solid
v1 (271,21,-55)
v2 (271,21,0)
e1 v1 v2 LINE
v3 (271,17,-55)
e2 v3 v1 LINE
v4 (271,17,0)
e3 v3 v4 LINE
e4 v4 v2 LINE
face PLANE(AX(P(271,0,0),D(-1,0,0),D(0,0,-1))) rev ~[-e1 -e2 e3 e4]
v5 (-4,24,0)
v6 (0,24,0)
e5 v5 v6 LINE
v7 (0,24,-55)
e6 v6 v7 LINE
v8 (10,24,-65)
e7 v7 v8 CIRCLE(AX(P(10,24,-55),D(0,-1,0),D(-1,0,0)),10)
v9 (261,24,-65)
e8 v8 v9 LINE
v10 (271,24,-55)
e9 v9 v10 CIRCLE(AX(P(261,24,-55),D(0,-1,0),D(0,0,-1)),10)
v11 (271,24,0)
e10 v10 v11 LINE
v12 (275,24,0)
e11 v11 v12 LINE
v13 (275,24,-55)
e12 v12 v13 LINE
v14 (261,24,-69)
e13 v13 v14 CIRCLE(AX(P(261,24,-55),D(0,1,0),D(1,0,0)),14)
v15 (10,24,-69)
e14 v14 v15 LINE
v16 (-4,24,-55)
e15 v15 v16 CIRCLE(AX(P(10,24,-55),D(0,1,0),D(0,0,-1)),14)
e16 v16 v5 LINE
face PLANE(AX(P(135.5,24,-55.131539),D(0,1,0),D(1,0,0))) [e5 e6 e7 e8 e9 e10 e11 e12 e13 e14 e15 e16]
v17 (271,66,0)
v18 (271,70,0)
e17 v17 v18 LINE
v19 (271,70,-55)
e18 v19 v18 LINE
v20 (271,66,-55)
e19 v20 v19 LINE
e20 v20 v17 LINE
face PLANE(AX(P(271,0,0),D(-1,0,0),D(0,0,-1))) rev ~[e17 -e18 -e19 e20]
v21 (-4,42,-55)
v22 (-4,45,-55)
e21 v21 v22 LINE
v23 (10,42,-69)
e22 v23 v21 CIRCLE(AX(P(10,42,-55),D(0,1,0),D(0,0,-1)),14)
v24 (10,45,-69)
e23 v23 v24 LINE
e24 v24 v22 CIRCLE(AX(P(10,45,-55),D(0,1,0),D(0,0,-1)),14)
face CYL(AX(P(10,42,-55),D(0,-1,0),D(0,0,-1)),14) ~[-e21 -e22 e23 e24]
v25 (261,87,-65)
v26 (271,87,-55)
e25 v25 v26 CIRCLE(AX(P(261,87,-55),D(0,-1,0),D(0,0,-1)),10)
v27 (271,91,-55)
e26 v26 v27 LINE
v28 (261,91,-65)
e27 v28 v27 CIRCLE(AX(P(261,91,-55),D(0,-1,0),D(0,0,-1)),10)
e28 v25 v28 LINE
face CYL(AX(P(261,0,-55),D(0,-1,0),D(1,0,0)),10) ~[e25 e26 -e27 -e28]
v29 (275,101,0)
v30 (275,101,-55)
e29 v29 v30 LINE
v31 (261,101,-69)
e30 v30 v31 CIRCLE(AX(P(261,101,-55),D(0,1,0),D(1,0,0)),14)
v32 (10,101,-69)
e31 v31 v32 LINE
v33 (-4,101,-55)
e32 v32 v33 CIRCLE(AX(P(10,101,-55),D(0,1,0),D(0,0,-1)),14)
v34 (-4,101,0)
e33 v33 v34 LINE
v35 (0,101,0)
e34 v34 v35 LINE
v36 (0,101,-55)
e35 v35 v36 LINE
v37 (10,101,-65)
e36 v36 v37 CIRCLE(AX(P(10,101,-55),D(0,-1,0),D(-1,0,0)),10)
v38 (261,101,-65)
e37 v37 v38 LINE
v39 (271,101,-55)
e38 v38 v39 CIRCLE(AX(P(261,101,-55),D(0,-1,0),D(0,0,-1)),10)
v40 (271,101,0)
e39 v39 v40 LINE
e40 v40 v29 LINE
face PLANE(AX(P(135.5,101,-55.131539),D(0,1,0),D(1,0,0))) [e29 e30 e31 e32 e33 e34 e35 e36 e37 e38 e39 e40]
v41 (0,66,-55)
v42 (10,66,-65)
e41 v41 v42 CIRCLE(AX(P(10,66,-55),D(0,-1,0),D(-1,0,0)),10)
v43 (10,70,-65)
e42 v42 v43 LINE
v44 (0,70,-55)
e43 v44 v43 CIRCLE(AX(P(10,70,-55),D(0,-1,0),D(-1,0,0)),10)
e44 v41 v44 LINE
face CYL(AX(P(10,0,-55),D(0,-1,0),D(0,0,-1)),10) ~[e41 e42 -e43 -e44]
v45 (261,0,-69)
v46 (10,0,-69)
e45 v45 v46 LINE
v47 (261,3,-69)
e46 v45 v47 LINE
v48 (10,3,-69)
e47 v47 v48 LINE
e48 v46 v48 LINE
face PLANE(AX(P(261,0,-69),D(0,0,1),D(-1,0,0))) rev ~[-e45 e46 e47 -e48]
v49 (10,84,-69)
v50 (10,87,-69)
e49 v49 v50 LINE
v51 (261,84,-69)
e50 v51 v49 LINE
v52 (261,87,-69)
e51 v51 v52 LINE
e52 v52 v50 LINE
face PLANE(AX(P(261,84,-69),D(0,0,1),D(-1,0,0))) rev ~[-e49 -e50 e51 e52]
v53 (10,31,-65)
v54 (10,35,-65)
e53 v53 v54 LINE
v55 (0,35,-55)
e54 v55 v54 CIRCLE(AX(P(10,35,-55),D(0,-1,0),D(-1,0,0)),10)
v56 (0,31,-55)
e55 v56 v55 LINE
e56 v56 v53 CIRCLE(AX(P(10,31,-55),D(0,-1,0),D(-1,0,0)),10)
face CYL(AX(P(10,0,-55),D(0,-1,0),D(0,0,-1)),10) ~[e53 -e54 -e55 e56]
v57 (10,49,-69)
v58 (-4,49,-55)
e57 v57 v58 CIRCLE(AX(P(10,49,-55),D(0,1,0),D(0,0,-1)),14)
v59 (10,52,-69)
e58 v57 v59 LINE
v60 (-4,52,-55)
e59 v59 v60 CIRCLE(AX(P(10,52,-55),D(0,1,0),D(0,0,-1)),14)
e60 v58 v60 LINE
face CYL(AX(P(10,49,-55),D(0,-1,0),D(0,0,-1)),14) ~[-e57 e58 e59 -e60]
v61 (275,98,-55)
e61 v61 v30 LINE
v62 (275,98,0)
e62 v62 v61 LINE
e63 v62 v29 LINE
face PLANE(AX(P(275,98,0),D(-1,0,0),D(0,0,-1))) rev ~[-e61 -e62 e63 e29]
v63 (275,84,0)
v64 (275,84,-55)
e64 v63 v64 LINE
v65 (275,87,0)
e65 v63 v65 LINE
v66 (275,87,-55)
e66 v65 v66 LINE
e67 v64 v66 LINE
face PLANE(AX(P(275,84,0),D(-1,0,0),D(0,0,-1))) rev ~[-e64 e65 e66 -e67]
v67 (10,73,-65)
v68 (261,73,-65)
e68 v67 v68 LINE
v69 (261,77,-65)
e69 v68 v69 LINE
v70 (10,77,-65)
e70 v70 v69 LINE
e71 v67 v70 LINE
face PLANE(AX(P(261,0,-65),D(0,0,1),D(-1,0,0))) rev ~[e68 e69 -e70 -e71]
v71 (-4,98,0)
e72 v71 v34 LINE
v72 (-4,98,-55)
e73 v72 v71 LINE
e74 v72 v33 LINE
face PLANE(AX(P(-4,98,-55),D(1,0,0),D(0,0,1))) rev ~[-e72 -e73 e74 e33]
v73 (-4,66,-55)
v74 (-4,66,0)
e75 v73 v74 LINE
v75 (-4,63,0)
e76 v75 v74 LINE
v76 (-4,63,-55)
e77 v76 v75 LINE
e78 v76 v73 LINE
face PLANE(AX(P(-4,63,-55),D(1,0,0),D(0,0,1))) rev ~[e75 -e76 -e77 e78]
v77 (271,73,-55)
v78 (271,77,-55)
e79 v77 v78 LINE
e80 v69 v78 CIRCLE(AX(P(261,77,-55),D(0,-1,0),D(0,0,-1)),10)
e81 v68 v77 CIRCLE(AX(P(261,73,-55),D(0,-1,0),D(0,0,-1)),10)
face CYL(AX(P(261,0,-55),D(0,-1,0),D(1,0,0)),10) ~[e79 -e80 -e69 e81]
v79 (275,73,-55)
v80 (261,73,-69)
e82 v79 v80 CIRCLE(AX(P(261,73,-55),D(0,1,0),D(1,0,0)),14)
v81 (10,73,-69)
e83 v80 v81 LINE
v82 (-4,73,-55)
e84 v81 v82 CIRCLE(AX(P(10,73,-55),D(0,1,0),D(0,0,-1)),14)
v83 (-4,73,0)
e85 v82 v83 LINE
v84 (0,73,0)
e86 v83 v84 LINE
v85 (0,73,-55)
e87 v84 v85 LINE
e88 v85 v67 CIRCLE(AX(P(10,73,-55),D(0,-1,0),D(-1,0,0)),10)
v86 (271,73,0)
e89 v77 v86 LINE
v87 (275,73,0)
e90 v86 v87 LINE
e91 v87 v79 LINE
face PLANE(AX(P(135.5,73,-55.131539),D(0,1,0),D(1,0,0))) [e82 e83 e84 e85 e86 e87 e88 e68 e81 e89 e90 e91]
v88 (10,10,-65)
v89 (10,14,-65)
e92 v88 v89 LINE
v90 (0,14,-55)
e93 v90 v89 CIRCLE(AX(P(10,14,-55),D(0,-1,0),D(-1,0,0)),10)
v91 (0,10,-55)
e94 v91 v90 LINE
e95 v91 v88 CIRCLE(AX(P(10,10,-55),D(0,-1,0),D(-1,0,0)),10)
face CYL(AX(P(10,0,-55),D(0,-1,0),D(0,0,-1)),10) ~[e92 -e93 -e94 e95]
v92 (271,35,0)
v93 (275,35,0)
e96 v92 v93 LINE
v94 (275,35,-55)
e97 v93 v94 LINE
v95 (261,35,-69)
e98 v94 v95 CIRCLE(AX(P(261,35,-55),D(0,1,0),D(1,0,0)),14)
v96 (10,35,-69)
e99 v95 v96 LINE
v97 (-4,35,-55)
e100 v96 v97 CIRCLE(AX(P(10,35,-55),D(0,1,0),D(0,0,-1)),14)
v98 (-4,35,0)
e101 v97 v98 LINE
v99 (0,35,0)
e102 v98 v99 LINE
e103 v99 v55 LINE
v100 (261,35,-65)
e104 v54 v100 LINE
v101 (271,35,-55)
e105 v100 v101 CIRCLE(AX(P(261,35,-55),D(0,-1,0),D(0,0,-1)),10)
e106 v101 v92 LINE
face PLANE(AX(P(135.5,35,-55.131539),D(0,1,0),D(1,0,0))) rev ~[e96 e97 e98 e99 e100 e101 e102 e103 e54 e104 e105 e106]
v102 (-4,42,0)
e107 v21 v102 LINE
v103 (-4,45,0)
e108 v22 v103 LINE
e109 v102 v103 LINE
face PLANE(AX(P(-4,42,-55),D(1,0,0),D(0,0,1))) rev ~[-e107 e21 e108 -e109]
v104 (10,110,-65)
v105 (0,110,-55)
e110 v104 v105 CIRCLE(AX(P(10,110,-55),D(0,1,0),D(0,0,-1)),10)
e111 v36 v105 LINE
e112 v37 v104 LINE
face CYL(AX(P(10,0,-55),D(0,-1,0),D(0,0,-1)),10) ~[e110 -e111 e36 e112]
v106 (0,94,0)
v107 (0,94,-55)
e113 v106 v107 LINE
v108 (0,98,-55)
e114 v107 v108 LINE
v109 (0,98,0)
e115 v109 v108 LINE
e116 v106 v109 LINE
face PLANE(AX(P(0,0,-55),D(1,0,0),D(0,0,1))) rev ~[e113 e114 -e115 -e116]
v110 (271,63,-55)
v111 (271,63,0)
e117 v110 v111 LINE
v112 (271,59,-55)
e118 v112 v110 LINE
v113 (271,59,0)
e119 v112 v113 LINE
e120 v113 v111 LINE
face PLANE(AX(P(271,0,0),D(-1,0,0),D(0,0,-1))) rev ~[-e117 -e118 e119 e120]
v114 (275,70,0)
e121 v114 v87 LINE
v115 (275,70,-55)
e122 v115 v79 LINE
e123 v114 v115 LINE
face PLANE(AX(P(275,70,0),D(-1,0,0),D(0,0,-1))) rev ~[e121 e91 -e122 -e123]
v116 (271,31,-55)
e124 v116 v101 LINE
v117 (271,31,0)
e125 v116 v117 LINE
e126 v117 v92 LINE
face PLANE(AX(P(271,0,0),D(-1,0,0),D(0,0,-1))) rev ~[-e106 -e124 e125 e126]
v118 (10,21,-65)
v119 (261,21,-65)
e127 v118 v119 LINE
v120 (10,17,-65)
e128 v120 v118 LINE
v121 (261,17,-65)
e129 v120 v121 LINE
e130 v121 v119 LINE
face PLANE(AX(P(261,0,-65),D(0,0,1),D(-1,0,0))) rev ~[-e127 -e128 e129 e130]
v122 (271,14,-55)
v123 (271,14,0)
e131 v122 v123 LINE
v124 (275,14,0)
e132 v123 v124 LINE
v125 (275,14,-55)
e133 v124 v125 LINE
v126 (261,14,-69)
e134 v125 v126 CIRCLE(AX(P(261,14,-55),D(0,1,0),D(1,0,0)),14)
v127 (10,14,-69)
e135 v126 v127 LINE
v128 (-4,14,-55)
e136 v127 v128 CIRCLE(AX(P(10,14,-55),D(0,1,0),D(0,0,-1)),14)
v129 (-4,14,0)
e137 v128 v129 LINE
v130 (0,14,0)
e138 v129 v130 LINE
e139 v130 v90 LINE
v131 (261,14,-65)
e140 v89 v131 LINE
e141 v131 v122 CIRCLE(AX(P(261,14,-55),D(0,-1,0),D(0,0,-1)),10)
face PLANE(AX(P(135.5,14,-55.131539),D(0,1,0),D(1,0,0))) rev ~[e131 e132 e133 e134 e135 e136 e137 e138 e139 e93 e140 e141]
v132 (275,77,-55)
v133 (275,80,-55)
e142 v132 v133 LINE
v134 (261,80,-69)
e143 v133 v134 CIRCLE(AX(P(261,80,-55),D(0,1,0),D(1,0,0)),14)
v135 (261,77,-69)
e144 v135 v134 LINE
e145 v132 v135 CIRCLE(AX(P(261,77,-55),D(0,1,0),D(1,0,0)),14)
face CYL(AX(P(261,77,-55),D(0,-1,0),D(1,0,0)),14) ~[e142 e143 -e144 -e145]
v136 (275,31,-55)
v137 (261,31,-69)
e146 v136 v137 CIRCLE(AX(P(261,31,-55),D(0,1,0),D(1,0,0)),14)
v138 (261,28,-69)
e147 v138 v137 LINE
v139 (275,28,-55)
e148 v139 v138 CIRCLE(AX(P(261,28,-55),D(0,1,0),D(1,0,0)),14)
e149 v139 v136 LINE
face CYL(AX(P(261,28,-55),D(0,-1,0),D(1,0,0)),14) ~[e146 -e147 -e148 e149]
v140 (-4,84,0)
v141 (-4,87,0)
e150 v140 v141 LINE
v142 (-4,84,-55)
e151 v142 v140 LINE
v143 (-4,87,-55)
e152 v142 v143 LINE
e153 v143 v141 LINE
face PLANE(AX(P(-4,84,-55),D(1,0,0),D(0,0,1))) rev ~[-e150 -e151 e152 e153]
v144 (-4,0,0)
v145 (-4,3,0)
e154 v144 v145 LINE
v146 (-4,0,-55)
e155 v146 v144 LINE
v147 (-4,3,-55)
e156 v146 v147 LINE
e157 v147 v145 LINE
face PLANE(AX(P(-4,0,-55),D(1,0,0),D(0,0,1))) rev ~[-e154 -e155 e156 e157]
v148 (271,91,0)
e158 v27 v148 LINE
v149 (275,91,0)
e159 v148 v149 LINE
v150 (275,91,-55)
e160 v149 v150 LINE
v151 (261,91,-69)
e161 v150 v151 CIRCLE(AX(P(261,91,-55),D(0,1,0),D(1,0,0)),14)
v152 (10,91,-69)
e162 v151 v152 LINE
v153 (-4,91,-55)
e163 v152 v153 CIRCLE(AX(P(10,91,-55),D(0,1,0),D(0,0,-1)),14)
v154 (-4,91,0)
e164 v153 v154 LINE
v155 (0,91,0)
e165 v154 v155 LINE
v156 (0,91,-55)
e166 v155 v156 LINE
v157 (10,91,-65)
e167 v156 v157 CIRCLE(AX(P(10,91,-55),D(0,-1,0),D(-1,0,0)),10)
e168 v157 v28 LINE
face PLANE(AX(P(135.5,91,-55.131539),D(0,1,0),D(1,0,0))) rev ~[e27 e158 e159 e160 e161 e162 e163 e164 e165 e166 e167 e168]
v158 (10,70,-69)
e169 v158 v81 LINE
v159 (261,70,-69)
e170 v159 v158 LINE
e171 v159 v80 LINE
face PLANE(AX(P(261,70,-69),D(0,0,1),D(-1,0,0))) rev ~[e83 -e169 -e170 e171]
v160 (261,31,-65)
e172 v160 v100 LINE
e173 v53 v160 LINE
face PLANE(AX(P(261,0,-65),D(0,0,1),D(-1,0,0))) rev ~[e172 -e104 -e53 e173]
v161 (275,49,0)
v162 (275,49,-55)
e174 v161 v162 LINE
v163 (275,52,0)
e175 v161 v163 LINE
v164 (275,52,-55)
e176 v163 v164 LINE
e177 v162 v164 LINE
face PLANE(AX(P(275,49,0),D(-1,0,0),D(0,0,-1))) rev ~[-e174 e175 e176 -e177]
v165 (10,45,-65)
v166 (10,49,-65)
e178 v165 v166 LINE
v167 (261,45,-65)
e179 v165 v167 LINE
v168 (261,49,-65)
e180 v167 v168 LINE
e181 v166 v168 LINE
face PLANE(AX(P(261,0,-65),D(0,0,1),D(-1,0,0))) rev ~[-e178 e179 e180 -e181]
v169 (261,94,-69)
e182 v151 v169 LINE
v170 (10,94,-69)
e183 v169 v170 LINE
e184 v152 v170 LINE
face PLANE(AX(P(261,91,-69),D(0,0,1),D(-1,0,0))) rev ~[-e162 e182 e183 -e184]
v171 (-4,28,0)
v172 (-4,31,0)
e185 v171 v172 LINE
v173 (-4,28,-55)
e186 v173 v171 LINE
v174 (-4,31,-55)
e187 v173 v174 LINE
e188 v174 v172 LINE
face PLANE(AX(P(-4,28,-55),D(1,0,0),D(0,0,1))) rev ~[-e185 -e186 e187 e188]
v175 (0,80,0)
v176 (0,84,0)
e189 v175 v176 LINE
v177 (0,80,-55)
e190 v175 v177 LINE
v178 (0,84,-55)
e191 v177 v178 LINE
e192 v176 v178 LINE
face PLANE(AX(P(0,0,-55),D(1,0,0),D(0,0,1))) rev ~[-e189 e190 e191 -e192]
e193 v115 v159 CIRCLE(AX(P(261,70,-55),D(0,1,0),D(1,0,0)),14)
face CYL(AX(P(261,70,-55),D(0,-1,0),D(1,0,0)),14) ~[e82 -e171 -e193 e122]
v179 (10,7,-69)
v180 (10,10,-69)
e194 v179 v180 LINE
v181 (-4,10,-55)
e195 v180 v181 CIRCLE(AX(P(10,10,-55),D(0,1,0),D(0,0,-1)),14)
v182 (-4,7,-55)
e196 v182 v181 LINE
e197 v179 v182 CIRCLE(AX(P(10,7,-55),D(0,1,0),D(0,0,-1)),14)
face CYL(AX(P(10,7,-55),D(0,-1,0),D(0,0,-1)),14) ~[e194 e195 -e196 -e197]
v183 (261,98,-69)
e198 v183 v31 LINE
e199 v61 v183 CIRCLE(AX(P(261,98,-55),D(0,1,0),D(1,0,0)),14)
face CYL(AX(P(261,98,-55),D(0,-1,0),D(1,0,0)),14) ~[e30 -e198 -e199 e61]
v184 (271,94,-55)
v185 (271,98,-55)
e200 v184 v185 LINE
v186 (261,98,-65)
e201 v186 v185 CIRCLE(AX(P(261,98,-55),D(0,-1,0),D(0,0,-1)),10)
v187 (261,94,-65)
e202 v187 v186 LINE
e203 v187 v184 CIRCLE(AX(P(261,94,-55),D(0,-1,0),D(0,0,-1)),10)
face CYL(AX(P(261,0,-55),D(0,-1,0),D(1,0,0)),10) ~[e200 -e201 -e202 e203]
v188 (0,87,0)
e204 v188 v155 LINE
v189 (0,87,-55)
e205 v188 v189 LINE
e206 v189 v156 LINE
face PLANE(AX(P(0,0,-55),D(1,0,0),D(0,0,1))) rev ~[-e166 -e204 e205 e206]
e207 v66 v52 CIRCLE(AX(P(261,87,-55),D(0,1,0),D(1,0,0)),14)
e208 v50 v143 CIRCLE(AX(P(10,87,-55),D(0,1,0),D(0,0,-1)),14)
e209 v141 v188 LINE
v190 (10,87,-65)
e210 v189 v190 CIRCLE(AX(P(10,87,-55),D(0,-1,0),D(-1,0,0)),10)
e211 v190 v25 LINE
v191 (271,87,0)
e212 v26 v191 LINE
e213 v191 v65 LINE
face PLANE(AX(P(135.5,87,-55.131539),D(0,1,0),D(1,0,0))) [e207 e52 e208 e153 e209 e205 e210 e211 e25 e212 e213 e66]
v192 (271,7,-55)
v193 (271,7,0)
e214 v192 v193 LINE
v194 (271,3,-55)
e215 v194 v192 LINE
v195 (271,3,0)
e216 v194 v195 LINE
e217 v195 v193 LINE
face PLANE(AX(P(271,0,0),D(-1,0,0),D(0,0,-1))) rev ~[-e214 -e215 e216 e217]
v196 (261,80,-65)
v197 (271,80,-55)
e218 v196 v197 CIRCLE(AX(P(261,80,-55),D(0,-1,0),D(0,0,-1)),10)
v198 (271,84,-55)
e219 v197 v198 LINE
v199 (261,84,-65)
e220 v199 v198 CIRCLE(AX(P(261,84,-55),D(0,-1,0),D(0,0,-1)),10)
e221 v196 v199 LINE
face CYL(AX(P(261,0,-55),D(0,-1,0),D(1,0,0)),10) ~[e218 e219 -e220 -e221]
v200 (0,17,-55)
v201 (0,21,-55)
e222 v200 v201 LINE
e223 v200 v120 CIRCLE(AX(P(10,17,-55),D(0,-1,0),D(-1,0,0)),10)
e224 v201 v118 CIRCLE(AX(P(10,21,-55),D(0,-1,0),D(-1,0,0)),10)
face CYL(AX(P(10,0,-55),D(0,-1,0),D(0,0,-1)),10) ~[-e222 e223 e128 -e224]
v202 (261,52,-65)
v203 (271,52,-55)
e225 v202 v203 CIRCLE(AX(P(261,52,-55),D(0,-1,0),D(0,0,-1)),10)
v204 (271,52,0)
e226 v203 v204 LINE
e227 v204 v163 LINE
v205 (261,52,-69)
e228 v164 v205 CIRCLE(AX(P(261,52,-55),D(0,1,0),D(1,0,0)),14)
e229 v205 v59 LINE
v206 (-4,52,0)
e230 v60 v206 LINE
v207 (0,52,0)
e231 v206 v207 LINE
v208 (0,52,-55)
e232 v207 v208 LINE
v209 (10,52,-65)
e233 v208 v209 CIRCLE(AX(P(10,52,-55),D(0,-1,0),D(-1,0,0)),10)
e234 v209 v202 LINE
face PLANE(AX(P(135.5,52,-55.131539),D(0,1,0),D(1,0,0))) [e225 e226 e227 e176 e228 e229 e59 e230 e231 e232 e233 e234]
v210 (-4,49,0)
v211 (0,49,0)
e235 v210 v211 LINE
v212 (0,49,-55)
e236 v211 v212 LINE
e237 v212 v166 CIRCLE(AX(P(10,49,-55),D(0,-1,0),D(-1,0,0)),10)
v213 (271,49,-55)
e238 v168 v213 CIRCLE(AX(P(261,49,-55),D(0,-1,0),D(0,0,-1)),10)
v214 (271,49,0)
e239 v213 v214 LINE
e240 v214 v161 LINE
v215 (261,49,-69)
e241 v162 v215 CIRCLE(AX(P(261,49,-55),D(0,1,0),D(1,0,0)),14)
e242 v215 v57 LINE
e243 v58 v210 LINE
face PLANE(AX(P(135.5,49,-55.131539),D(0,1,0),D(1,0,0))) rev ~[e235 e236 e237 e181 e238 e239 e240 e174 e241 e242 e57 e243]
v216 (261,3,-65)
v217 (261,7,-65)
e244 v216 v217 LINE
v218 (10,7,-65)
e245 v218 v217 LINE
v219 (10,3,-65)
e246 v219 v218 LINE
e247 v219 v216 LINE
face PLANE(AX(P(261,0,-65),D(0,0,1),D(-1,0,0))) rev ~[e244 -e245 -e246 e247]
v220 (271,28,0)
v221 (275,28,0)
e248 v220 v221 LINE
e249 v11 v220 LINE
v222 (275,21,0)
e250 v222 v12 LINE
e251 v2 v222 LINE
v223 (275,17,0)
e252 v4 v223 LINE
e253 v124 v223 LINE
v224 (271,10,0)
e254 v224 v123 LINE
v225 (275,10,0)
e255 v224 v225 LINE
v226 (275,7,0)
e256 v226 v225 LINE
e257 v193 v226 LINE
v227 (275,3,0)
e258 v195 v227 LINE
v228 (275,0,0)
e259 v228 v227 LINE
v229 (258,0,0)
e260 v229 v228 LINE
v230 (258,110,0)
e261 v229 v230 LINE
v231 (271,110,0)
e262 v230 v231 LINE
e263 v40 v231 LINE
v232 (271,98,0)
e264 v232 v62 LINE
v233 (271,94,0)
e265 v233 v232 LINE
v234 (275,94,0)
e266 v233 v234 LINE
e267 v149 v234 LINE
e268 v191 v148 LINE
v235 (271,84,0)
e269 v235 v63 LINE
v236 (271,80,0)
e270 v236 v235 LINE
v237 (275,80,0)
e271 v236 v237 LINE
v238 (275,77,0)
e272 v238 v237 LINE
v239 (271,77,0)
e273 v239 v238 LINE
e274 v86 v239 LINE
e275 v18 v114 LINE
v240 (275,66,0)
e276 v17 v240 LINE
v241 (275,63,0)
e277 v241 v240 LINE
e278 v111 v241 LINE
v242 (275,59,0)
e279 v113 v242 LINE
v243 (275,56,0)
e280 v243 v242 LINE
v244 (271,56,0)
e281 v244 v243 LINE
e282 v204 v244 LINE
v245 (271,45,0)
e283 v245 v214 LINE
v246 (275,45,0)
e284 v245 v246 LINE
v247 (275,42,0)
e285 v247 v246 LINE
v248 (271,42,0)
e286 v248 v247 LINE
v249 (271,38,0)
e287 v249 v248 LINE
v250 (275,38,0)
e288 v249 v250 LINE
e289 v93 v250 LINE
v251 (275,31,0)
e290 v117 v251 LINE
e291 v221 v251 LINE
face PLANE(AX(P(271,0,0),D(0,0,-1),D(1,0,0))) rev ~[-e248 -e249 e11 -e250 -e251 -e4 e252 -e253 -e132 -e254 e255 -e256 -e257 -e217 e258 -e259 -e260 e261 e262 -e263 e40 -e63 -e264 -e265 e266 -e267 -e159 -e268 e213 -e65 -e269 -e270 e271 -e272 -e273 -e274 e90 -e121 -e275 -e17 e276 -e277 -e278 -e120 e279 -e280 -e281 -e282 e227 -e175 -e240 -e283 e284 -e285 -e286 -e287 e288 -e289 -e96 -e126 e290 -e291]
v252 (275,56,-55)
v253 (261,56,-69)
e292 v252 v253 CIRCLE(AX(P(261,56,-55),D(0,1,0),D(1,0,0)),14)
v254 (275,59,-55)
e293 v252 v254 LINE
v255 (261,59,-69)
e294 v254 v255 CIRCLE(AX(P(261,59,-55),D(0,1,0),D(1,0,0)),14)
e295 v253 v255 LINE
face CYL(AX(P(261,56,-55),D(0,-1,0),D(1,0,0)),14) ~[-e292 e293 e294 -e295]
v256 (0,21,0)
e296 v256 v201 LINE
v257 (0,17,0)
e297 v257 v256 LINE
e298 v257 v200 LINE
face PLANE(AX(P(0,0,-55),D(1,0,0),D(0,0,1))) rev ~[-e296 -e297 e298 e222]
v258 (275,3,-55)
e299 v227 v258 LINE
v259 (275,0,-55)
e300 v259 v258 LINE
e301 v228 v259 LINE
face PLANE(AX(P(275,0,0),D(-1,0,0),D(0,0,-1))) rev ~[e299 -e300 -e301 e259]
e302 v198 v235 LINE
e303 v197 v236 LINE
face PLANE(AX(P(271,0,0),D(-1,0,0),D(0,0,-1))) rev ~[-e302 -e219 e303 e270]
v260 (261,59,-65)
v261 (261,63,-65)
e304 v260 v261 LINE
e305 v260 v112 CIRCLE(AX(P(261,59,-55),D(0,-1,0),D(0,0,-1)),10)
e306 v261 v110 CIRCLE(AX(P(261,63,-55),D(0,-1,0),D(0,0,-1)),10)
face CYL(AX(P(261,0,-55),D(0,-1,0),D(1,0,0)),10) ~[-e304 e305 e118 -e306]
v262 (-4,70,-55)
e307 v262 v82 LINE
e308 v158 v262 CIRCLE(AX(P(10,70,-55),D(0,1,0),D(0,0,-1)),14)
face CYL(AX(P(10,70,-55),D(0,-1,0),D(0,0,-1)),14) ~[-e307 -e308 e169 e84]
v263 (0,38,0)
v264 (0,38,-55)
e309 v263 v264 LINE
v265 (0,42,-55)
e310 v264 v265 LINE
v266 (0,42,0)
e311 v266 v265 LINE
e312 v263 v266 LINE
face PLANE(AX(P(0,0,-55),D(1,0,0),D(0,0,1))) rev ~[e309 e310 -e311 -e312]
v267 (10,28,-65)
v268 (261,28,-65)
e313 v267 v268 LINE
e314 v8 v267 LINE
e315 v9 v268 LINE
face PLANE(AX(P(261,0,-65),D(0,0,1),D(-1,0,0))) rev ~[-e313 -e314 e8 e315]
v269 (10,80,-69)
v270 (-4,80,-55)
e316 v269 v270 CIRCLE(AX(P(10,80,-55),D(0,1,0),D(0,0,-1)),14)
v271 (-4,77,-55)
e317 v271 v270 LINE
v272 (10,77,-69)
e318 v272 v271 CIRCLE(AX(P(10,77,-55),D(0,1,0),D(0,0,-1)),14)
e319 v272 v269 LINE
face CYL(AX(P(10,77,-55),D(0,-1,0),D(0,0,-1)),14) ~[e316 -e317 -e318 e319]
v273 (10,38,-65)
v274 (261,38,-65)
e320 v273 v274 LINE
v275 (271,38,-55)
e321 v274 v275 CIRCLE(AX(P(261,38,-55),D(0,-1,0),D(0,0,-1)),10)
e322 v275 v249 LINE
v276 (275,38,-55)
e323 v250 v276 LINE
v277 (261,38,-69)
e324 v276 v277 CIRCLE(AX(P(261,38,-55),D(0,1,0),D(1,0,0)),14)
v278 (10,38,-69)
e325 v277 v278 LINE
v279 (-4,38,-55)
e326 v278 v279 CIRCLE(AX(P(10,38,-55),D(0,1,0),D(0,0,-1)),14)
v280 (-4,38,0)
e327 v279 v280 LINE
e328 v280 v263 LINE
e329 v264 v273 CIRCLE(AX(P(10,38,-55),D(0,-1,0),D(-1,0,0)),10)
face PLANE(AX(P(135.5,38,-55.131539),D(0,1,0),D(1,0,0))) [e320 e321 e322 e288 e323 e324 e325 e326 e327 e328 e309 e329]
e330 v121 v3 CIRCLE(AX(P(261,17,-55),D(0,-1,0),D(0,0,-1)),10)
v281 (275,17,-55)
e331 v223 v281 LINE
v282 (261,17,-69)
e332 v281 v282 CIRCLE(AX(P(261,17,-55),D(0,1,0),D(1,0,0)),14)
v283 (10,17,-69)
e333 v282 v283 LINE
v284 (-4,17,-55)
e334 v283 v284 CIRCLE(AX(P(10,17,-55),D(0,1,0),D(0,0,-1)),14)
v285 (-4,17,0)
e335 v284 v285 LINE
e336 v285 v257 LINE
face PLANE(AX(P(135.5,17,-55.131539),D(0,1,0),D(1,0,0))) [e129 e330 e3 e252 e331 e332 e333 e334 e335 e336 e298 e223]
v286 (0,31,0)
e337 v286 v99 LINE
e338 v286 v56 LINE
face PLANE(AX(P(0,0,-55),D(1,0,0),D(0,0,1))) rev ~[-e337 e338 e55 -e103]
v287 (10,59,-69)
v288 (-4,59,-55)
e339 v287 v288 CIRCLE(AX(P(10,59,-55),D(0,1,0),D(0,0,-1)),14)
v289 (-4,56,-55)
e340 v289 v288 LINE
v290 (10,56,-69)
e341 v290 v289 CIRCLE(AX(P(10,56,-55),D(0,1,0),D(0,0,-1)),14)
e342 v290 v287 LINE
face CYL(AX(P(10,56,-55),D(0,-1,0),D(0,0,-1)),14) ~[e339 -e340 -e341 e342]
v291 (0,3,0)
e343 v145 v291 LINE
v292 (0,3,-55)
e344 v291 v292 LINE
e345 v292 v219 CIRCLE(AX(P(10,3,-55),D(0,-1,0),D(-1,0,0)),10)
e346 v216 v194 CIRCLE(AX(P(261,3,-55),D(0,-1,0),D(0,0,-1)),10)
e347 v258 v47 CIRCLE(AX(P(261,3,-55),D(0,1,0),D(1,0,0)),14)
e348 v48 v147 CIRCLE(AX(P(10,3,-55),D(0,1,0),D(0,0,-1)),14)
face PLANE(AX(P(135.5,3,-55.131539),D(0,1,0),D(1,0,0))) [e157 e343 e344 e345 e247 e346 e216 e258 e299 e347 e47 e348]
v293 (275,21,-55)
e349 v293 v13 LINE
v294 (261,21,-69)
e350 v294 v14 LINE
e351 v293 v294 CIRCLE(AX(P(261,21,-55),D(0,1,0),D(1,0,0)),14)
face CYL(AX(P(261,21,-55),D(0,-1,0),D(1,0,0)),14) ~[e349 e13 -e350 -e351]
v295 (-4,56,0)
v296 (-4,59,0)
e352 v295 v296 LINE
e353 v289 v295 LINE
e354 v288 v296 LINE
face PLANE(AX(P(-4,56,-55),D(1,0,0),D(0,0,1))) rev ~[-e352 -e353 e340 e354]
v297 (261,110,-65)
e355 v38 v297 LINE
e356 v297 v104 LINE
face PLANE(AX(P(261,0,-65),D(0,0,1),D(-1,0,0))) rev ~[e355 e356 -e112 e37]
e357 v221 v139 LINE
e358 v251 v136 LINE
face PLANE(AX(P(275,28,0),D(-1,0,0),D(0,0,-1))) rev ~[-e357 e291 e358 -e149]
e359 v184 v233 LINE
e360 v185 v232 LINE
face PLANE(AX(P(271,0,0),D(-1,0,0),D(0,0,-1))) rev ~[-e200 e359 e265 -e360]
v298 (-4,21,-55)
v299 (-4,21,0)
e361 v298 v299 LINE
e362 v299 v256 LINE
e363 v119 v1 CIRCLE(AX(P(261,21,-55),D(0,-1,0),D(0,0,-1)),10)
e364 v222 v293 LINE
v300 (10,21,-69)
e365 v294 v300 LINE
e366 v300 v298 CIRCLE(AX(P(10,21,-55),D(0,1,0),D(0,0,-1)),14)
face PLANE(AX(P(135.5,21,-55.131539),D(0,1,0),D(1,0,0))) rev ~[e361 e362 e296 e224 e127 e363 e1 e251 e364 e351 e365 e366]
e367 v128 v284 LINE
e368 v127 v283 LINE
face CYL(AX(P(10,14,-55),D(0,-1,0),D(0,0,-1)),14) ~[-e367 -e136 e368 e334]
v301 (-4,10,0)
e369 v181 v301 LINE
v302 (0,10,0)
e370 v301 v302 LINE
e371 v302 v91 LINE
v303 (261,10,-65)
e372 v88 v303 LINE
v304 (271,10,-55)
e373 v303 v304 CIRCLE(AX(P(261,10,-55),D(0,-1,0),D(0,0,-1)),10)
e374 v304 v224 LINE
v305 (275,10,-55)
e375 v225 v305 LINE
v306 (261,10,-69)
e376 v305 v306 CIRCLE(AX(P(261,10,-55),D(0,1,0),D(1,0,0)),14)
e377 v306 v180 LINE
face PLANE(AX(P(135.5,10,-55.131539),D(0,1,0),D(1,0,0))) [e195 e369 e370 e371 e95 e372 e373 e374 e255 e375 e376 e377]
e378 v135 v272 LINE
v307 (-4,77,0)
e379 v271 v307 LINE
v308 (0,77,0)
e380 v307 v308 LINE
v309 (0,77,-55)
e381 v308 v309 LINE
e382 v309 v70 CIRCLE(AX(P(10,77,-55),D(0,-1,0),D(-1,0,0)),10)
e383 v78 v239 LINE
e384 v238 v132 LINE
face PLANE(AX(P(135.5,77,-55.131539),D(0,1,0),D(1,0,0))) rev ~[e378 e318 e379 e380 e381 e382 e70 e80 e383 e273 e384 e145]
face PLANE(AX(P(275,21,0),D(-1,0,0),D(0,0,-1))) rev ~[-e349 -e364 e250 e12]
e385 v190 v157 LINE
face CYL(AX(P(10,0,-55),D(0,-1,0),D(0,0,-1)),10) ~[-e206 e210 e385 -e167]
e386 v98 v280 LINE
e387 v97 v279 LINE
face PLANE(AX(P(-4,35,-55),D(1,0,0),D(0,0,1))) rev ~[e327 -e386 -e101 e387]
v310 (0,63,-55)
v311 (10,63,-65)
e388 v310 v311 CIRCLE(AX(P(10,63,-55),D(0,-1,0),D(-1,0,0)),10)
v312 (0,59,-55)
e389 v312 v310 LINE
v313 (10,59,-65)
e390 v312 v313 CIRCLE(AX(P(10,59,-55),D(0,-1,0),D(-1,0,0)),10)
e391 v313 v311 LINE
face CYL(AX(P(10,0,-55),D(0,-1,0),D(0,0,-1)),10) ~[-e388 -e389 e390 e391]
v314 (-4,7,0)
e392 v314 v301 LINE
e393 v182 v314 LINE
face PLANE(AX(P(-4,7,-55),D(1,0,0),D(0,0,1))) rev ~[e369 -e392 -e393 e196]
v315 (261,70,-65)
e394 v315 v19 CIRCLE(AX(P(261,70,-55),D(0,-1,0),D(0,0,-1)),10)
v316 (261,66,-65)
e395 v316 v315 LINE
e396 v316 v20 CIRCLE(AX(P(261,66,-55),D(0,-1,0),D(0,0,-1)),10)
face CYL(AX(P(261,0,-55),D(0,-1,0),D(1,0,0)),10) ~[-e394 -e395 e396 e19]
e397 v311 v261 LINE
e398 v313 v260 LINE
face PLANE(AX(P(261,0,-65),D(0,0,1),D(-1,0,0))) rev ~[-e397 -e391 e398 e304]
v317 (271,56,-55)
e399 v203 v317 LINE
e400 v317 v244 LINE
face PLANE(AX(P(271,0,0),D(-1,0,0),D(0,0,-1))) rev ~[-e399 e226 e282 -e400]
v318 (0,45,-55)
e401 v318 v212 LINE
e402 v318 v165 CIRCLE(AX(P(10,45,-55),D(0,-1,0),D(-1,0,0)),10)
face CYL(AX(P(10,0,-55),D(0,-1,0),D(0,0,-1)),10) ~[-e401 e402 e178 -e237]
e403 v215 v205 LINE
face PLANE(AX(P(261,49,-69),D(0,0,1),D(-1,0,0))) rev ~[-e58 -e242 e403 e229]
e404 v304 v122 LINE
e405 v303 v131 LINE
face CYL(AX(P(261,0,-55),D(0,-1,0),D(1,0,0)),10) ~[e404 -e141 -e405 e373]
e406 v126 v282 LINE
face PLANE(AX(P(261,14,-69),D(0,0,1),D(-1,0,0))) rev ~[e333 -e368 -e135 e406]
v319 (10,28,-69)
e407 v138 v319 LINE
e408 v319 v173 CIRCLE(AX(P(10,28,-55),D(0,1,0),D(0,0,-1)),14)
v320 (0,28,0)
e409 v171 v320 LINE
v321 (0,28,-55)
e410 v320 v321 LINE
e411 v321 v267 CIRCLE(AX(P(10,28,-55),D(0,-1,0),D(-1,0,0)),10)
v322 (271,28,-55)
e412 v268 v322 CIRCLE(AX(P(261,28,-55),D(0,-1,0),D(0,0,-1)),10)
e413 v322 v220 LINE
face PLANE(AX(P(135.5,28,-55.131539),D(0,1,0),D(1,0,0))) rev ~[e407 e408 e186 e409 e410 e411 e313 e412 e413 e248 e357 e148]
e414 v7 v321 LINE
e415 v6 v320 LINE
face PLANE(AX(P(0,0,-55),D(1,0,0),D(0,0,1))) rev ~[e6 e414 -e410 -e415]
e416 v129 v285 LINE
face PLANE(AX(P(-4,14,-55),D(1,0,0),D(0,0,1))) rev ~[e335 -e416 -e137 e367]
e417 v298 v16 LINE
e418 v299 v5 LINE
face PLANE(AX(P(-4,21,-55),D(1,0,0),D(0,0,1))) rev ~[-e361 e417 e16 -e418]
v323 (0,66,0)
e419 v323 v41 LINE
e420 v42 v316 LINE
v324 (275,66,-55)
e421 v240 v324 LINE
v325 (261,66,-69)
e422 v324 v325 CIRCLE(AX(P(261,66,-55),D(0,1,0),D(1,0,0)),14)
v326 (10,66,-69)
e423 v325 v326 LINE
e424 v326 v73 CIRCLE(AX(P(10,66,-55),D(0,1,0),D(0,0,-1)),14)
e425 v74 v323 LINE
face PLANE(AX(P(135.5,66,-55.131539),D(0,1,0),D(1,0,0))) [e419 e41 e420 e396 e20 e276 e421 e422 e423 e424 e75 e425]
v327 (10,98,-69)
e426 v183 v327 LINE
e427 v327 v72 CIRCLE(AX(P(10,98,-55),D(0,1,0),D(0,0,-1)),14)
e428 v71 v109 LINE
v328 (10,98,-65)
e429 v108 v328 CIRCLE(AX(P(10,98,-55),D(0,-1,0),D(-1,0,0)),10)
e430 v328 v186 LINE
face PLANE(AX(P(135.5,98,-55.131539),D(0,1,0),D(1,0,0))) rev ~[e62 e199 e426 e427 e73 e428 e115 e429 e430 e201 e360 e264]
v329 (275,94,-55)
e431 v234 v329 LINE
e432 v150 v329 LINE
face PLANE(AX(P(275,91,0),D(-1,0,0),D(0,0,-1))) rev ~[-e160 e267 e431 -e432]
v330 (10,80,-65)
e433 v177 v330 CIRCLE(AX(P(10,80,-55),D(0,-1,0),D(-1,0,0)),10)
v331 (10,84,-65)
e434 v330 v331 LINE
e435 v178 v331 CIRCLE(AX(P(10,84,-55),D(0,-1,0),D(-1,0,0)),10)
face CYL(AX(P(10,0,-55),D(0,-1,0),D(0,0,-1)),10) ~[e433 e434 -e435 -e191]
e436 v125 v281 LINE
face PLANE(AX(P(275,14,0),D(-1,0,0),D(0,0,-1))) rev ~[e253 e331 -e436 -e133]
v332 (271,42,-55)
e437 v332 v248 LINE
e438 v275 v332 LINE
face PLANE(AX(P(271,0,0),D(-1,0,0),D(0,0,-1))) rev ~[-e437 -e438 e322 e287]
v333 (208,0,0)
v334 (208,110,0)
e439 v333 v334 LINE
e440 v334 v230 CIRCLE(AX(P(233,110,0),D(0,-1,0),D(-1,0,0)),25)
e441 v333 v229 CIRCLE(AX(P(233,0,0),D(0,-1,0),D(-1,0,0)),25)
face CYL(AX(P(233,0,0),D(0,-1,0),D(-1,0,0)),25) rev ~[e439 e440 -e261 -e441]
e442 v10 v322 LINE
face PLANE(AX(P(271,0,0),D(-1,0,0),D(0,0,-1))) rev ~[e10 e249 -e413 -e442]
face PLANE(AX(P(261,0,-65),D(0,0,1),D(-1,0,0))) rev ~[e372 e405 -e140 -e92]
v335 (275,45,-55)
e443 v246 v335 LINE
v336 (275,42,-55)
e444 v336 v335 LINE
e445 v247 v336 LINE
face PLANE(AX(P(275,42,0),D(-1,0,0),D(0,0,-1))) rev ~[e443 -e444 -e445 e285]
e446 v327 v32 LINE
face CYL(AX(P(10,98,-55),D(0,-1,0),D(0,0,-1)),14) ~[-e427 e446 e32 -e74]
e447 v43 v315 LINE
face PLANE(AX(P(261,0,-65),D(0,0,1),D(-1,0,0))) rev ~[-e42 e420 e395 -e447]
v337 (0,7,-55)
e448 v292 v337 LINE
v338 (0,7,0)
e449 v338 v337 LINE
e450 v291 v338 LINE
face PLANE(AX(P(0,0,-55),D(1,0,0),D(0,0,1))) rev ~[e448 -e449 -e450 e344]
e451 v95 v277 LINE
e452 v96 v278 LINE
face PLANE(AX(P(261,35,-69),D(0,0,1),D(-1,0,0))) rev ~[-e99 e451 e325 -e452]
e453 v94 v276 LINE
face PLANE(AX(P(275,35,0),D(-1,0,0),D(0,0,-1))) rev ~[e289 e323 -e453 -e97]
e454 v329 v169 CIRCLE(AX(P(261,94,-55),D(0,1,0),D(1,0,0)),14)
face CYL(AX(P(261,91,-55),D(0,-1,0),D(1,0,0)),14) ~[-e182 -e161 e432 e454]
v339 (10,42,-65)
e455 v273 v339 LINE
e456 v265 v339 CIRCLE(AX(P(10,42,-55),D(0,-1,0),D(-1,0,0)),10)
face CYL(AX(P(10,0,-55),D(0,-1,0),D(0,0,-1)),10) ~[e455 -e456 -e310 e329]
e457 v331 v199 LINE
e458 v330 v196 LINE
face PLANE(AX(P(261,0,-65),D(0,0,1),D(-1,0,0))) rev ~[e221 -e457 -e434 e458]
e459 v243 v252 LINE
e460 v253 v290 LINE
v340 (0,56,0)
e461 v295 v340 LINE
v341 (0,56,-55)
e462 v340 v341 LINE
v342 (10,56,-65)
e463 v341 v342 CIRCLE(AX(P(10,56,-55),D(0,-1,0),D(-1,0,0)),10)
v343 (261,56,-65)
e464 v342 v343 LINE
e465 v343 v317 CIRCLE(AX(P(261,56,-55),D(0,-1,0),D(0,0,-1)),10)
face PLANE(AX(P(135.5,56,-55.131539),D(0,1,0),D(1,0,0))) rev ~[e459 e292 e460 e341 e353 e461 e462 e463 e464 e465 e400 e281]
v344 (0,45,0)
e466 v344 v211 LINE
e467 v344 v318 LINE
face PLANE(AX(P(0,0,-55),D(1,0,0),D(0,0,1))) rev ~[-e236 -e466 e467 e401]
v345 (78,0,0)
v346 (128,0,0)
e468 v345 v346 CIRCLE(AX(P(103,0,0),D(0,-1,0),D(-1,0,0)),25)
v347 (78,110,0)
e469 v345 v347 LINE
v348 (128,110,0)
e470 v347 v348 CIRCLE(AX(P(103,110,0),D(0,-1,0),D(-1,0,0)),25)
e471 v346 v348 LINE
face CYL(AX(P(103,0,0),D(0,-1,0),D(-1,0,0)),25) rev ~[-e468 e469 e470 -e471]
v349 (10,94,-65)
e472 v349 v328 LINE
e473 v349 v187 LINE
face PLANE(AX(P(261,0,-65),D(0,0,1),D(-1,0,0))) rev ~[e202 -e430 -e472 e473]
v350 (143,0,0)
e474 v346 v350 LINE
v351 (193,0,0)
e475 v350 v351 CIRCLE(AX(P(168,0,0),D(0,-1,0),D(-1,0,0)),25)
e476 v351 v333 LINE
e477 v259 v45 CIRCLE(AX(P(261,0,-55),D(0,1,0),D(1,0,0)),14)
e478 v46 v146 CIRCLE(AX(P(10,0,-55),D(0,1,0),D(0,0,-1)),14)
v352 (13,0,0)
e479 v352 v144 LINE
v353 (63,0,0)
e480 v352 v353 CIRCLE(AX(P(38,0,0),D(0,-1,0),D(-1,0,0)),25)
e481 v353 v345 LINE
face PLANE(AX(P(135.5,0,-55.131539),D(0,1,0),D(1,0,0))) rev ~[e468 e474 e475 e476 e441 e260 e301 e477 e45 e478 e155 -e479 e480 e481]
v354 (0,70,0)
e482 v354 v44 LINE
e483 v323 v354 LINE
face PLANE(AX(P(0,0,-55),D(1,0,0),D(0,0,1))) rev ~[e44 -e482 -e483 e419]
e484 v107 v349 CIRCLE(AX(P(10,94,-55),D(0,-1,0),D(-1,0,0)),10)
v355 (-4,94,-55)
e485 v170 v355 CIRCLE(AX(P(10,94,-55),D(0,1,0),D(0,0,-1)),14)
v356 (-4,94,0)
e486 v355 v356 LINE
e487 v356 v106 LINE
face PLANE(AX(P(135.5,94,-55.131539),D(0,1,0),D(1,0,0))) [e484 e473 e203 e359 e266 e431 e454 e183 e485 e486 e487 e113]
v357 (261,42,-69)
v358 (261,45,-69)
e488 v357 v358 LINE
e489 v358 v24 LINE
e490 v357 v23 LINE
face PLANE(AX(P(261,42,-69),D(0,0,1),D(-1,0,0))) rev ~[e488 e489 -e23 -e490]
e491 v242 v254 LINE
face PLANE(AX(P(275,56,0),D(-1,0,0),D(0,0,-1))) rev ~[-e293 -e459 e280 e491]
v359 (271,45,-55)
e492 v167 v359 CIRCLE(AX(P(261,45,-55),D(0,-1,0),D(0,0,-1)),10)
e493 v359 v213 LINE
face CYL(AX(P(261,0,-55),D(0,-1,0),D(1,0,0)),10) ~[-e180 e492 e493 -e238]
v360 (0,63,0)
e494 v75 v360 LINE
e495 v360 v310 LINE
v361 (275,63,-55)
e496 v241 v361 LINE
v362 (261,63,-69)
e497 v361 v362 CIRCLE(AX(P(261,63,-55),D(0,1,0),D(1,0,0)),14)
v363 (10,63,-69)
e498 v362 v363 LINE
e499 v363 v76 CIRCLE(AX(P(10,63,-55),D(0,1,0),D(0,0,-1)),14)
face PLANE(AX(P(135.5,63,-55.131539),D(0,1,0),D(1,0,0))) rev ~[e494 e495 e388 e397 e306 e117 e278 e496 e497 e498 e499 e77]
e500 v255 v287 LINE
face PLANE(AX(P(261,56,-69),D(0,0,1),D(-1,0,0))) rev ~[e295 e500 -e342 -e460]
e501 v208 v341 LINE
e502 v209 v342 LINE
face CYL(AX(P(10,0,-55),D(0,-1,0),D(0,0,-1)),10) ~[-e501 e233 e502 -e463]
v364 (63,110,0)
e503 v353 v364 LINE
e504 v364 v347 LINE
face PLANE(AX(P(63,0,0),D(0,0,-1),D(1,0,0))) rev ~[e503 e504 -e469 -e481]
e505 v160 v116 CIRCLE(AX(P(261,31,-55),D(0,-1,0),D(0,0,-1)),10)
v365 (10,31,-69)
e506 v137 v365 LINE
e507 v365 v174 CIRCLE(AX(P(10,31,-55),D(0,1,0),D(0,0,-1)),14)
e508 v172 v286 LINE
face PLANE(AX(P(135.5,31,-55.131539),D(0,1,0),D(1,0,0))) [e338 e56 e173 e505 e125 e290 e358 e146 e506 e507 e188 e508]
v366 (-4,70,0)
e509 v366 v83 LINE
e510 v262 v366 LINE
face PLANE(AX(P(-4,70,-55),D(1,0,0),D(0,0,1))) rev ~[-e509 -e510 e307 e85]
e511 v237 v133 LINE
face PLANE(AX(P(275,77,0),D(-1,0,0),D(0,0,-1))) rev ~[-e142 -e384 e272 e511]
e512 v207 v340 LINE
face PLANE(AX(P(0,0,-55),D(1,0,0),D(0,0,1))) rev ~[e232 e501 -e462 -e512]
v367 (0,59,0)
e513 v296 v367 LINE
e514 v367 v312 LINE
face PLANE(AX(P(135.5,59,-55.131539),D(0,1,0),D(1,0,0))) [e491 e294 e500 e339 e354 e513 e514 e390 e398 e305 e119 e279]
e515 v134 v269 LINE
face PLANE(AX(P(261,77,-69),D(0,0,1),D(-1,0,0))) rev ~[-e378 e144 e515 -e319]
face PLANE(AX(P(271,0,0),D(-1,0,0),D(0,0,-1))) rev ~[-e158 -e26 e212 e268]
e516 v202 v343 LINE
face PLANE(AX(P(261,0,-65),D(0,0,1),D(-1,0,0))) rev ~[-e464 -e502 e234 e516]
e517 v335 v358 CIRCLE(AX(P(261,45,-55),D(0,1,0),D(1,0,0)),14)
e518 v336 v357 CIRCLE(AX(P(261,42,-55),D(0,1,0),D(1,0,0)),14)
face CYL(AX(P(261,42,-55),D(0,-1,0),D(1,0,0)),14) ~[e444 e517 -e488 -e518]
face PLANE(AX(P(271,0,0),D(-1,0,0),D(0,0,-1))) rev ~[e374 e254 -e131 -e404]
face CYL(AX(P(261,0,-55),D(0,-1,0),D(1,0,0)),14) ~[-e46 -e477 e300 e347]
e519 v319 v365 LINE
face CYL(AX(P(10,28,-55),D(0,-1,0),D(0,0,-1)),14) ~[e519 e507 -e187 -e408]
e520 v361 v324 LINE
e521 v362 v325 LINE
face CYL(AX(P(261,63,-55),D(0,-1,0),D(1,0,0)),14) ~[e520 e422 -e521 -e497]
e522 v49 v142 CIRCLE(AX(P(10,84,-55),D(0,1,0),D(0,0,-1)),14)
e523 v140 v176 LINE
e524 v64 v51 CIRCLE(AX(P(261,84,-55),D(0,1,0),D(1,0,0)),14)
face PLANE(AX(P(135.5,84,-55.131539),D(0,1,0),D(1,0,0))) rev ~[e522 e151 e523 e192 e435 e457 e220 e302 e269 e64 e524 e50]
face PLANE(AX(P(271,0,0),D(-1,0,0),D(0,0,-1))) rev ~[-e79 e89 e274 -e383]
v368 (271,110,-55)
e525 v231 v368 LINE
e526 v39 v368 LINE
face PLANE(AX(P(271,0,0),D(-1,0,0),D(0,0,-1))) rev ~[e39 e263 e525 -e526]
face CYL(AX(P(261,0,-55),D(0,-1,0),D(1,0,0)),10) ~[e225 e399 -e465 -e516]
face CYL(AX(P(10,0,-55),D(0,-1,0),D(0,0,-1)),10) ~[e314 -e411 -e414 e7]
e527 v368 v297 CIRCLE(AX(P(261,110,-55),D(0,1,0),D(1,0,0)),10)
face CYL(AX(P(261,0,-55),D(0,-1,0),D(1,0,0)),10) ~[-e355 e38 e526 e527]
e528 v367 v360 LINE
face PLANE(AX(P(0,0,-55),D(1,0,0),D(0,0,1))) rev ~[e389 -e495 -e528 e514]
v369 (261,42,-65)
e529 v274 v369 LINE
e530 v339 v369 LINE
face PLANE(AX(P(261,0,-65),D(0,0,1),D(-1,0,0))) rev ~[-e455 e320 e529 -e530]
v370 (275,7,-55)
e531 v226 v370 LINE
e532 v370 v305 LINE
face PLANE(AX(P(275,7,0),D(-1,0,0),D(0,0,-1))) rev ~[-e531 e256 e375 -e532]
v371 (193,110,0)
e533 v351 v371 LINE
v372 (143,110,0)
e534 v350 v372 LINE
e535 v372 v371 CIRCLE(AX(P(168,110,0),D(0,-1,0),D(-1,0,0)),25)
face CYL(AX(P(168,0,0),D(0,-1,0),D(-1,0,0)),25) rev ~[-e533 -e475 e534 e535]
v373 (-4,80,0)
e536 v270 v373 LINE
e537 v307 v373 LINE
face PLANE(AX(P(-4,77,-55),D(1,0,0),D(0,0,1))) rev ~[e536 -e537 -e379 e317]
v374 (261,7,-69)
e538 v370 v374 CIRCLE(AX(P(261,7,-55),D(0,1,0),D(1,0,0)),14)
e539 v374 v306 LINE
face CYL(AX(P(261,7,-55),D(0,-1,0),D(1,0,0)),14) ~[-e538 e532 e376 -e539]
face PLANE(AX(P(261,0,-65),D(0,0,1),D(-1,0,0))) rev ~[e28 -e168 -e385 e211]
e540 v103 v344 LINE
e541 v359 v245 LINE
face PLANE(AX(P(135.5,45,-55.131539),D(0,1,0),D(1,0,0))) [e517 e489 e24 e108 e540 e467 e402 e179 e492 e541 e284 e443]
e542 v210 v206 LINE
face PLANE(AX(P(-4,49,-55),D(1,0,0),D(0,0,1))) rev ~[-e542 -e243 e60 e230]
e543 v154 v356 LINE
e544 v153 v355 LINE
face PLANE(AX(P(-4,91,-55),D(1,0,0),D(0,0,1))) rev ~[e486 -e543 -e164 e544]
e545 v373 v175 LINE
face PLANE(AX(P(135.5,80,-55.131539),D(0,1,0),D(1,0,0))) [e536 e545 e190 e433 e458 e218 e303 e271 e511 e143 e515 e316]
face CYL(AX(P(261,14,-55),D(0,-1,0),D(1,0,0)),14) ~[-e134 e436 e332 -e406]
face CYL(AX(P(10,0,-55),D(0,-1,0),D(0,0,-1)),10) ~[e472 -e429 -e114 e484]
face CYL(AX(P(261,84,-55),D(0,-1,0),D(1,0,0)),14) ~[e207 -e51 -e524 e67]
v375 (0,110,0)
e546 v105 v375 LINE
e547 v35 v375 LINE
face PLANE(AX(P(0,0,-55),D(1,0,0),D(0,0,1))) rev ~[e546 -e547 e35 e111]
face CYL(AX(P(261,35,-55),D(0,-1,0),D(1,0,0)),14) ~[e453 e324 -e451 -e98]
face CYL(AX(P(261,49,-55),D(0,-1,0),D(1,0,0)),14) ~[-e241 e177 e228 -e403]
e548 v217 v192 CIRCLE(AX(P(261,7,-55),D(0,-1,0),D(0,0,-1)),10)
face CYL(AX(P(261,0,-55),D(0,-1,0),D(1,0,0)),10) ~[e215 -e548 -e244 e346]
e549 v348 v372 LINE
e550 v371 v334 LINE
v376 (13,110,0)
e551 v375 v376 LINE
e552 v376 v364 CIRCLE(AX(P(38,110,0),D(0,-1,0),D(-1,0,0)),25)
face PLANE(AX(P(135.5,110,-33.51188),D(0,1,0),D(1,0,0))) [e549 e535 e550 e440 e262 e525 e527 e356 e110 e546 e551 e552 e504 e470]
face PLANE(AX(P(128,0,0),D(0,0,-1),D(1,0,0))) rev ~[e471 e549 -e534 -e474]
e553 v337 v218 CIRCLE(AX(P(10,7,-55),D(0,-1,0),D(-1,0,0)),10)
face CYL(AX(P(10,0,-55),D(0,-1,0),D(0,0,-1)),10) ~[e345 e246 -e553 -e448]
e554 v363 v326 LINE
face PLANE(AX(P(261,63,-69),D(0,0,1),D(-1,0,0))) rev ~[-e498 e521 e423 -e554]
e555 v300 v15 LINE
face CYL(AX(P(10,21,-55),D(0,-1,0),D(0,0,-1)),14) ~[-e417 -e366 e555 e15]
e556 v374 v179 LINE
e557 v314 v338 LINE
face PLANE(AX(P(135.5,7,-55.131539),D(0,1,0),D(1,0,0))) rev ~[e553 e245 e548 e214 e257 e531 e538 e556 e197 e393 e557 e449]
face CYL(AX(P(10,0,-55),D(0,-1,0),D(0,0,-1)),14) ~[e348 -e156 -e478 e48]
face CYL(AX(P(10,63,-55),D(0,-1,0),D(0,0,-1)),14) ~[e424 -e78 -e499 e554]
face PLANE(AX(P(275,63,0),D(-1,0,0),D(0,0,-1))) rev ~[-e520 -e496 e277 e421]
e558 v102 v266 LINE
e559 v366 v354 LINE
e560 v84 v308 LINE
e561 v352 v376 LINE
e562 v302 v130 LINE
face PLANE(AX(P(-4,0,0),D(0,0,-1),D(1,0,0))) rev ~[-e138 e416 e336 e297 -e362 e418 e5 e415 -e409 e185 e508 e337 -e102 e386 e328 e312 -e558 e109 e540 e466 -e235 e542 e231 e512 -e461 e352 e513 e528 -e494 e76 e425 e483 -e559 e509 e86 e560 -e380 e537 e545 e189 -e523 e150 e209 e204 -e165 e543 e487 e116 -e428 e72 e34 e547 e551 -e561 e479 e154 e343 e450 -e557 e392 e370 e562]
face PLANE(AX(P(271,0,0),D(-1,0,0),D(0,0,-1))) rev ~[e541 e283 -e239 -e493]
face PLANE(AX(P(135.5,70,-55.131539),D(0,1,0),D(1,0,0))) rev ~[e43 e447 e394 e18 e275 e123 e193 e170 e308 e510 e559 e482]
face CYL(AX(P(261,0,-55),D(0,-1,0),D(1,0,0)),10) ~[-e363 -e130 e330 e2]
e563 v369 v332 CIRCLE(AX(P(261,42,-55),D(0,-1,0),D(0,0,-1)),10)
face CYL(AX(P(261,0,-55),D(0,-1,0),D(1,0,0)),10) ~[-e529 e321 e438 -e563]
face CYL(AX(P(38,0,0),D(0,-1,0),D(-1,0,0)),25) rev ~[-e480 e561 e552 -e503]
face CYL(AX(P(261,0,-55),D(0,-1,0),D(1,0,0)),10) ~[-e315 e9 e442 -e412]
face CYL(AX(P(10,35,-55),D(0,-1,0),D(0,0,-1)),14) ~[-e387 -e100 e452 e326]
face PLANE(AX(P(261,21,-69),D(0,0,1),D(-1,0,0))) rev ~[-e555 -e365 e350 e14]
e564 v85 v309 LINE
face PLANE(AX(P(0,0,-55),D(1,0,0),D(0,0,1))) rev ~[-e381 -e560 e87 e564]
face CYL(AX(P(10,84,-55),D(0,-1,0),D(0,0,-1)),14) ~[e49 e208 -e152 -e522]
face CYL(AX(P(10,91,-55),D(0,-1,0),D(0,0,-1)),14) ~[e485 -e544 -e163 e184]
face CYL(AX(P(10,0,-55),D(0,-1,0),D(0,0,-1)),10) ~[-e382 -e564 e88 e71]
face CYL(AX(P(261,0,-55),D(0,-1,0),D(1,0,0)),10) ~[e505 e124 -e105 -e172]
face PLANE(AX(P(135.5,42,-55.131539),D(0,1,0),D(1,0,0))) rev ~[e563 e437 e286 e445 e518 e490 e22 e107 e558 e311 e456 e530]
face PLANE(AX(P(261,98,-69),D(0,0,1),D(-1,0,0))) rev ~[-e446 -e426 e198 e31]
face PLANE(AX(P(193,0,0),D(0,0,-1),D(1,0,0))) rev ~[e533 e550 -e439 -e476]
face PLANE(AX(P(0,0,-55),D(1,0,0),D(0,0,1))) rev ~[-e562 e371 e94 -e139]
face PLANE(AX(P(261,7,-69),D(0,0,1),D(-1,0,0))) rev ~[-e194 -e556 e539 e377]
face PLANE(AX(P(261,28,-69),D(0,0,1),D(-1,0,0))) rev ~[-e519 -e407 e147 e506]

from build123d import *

# Parameters (mm, degrees)
UPPER_BLOCK_BODY_DEPTH             = 110
END_SERRATION_RIB_DEPTH            = 3
SERRATION_RIB_PATTERN_15X7MM_COUNT = 15
SERRATION_RIB_PATTERN_15X7MM_PITCH = 7


with BuildPart() as part:
    # Block Profile Sketch → Upper Block Body (new body)
    with BuildSketch(Plane(origin=(0, 0, 0), x_dir=(1, 0, 0), z_dir=(0, 1, 0))):
        with BuildLine():
            Line((0, 0), (13, 0))
            ThreePointArc((13, 0), (38, 25), (63, 0))
            Line((63, 0), (78, 0))
            ThreePointArc((78, 0), (103, 25), (128, 0))
            Line((128, 0), (143, 0))
            ThreePointArc((143, 0), (168, 25), (193, 0))
            Line((193, 0), (208, 0))
            ThreePointArc((208, 0), (233, 25), (258, 0))
            Line((258, 0), (271, 0))
            Line((271, 0), (271, 55))
            ThreePointArc((271, 55), (268.071067812, 62.071067812), (261, 65))
            Line((261, 65), (10, 65))
            ThreePointArc((10, 65), (2.928932188, 62.071067812), (0, 55))
            Line((0, 55), (0, 0))
        make_face()
    extrude(amount=UPPER_BLOCK_BODY_DEPTH)

    # End Serration Sketch → End Serration Rib (add)
    with BuildSketch(Plane(origin=(0, 0, 0), x_dir=(1, 0, 0), z_dir=(0, 1, 0))):
        with BuildLine():
            Line((275, 0), (275, 55))
            ThreePointArc((275, 55), (270.899494937, 64.899494937), (261, 69))
            Line((261, 69), (10, 69))
            ThreePointArc((10, 69), (0.100505063, 64.899494937), (-4, 55))
            Line((-4, 55), (-4, 0))
            Line((-4, 0), (0, 0))
            Line((0, 0), (0, 55))
            ThreePointArc((0, 55), (2.928932188, 62.071067812), (10, 65))
            Line((10, 65), (261, 65))
            ThreePointArc((261, 65), (268.071067812, 62.071067812), (271, 55))
            Line((271, 55), (271, 0))
            Line((271, 0), (275, 0))
        make_face()
    end_serration_rib = extrude(amount=END_SERRATION_RIB_DEPTH)

    # Serration Rib Pattern 15x7mm: End Serration Rib ×15
    with Locations(*[(0, i * SERRATION_RIB_PATTERN_15X7MM_PITCH, 0) for i in range(1, SERRATION_RIB_PATTERN_15X7MM_COUNT)]):
        add(end_serration_rib)


solid = part.part
